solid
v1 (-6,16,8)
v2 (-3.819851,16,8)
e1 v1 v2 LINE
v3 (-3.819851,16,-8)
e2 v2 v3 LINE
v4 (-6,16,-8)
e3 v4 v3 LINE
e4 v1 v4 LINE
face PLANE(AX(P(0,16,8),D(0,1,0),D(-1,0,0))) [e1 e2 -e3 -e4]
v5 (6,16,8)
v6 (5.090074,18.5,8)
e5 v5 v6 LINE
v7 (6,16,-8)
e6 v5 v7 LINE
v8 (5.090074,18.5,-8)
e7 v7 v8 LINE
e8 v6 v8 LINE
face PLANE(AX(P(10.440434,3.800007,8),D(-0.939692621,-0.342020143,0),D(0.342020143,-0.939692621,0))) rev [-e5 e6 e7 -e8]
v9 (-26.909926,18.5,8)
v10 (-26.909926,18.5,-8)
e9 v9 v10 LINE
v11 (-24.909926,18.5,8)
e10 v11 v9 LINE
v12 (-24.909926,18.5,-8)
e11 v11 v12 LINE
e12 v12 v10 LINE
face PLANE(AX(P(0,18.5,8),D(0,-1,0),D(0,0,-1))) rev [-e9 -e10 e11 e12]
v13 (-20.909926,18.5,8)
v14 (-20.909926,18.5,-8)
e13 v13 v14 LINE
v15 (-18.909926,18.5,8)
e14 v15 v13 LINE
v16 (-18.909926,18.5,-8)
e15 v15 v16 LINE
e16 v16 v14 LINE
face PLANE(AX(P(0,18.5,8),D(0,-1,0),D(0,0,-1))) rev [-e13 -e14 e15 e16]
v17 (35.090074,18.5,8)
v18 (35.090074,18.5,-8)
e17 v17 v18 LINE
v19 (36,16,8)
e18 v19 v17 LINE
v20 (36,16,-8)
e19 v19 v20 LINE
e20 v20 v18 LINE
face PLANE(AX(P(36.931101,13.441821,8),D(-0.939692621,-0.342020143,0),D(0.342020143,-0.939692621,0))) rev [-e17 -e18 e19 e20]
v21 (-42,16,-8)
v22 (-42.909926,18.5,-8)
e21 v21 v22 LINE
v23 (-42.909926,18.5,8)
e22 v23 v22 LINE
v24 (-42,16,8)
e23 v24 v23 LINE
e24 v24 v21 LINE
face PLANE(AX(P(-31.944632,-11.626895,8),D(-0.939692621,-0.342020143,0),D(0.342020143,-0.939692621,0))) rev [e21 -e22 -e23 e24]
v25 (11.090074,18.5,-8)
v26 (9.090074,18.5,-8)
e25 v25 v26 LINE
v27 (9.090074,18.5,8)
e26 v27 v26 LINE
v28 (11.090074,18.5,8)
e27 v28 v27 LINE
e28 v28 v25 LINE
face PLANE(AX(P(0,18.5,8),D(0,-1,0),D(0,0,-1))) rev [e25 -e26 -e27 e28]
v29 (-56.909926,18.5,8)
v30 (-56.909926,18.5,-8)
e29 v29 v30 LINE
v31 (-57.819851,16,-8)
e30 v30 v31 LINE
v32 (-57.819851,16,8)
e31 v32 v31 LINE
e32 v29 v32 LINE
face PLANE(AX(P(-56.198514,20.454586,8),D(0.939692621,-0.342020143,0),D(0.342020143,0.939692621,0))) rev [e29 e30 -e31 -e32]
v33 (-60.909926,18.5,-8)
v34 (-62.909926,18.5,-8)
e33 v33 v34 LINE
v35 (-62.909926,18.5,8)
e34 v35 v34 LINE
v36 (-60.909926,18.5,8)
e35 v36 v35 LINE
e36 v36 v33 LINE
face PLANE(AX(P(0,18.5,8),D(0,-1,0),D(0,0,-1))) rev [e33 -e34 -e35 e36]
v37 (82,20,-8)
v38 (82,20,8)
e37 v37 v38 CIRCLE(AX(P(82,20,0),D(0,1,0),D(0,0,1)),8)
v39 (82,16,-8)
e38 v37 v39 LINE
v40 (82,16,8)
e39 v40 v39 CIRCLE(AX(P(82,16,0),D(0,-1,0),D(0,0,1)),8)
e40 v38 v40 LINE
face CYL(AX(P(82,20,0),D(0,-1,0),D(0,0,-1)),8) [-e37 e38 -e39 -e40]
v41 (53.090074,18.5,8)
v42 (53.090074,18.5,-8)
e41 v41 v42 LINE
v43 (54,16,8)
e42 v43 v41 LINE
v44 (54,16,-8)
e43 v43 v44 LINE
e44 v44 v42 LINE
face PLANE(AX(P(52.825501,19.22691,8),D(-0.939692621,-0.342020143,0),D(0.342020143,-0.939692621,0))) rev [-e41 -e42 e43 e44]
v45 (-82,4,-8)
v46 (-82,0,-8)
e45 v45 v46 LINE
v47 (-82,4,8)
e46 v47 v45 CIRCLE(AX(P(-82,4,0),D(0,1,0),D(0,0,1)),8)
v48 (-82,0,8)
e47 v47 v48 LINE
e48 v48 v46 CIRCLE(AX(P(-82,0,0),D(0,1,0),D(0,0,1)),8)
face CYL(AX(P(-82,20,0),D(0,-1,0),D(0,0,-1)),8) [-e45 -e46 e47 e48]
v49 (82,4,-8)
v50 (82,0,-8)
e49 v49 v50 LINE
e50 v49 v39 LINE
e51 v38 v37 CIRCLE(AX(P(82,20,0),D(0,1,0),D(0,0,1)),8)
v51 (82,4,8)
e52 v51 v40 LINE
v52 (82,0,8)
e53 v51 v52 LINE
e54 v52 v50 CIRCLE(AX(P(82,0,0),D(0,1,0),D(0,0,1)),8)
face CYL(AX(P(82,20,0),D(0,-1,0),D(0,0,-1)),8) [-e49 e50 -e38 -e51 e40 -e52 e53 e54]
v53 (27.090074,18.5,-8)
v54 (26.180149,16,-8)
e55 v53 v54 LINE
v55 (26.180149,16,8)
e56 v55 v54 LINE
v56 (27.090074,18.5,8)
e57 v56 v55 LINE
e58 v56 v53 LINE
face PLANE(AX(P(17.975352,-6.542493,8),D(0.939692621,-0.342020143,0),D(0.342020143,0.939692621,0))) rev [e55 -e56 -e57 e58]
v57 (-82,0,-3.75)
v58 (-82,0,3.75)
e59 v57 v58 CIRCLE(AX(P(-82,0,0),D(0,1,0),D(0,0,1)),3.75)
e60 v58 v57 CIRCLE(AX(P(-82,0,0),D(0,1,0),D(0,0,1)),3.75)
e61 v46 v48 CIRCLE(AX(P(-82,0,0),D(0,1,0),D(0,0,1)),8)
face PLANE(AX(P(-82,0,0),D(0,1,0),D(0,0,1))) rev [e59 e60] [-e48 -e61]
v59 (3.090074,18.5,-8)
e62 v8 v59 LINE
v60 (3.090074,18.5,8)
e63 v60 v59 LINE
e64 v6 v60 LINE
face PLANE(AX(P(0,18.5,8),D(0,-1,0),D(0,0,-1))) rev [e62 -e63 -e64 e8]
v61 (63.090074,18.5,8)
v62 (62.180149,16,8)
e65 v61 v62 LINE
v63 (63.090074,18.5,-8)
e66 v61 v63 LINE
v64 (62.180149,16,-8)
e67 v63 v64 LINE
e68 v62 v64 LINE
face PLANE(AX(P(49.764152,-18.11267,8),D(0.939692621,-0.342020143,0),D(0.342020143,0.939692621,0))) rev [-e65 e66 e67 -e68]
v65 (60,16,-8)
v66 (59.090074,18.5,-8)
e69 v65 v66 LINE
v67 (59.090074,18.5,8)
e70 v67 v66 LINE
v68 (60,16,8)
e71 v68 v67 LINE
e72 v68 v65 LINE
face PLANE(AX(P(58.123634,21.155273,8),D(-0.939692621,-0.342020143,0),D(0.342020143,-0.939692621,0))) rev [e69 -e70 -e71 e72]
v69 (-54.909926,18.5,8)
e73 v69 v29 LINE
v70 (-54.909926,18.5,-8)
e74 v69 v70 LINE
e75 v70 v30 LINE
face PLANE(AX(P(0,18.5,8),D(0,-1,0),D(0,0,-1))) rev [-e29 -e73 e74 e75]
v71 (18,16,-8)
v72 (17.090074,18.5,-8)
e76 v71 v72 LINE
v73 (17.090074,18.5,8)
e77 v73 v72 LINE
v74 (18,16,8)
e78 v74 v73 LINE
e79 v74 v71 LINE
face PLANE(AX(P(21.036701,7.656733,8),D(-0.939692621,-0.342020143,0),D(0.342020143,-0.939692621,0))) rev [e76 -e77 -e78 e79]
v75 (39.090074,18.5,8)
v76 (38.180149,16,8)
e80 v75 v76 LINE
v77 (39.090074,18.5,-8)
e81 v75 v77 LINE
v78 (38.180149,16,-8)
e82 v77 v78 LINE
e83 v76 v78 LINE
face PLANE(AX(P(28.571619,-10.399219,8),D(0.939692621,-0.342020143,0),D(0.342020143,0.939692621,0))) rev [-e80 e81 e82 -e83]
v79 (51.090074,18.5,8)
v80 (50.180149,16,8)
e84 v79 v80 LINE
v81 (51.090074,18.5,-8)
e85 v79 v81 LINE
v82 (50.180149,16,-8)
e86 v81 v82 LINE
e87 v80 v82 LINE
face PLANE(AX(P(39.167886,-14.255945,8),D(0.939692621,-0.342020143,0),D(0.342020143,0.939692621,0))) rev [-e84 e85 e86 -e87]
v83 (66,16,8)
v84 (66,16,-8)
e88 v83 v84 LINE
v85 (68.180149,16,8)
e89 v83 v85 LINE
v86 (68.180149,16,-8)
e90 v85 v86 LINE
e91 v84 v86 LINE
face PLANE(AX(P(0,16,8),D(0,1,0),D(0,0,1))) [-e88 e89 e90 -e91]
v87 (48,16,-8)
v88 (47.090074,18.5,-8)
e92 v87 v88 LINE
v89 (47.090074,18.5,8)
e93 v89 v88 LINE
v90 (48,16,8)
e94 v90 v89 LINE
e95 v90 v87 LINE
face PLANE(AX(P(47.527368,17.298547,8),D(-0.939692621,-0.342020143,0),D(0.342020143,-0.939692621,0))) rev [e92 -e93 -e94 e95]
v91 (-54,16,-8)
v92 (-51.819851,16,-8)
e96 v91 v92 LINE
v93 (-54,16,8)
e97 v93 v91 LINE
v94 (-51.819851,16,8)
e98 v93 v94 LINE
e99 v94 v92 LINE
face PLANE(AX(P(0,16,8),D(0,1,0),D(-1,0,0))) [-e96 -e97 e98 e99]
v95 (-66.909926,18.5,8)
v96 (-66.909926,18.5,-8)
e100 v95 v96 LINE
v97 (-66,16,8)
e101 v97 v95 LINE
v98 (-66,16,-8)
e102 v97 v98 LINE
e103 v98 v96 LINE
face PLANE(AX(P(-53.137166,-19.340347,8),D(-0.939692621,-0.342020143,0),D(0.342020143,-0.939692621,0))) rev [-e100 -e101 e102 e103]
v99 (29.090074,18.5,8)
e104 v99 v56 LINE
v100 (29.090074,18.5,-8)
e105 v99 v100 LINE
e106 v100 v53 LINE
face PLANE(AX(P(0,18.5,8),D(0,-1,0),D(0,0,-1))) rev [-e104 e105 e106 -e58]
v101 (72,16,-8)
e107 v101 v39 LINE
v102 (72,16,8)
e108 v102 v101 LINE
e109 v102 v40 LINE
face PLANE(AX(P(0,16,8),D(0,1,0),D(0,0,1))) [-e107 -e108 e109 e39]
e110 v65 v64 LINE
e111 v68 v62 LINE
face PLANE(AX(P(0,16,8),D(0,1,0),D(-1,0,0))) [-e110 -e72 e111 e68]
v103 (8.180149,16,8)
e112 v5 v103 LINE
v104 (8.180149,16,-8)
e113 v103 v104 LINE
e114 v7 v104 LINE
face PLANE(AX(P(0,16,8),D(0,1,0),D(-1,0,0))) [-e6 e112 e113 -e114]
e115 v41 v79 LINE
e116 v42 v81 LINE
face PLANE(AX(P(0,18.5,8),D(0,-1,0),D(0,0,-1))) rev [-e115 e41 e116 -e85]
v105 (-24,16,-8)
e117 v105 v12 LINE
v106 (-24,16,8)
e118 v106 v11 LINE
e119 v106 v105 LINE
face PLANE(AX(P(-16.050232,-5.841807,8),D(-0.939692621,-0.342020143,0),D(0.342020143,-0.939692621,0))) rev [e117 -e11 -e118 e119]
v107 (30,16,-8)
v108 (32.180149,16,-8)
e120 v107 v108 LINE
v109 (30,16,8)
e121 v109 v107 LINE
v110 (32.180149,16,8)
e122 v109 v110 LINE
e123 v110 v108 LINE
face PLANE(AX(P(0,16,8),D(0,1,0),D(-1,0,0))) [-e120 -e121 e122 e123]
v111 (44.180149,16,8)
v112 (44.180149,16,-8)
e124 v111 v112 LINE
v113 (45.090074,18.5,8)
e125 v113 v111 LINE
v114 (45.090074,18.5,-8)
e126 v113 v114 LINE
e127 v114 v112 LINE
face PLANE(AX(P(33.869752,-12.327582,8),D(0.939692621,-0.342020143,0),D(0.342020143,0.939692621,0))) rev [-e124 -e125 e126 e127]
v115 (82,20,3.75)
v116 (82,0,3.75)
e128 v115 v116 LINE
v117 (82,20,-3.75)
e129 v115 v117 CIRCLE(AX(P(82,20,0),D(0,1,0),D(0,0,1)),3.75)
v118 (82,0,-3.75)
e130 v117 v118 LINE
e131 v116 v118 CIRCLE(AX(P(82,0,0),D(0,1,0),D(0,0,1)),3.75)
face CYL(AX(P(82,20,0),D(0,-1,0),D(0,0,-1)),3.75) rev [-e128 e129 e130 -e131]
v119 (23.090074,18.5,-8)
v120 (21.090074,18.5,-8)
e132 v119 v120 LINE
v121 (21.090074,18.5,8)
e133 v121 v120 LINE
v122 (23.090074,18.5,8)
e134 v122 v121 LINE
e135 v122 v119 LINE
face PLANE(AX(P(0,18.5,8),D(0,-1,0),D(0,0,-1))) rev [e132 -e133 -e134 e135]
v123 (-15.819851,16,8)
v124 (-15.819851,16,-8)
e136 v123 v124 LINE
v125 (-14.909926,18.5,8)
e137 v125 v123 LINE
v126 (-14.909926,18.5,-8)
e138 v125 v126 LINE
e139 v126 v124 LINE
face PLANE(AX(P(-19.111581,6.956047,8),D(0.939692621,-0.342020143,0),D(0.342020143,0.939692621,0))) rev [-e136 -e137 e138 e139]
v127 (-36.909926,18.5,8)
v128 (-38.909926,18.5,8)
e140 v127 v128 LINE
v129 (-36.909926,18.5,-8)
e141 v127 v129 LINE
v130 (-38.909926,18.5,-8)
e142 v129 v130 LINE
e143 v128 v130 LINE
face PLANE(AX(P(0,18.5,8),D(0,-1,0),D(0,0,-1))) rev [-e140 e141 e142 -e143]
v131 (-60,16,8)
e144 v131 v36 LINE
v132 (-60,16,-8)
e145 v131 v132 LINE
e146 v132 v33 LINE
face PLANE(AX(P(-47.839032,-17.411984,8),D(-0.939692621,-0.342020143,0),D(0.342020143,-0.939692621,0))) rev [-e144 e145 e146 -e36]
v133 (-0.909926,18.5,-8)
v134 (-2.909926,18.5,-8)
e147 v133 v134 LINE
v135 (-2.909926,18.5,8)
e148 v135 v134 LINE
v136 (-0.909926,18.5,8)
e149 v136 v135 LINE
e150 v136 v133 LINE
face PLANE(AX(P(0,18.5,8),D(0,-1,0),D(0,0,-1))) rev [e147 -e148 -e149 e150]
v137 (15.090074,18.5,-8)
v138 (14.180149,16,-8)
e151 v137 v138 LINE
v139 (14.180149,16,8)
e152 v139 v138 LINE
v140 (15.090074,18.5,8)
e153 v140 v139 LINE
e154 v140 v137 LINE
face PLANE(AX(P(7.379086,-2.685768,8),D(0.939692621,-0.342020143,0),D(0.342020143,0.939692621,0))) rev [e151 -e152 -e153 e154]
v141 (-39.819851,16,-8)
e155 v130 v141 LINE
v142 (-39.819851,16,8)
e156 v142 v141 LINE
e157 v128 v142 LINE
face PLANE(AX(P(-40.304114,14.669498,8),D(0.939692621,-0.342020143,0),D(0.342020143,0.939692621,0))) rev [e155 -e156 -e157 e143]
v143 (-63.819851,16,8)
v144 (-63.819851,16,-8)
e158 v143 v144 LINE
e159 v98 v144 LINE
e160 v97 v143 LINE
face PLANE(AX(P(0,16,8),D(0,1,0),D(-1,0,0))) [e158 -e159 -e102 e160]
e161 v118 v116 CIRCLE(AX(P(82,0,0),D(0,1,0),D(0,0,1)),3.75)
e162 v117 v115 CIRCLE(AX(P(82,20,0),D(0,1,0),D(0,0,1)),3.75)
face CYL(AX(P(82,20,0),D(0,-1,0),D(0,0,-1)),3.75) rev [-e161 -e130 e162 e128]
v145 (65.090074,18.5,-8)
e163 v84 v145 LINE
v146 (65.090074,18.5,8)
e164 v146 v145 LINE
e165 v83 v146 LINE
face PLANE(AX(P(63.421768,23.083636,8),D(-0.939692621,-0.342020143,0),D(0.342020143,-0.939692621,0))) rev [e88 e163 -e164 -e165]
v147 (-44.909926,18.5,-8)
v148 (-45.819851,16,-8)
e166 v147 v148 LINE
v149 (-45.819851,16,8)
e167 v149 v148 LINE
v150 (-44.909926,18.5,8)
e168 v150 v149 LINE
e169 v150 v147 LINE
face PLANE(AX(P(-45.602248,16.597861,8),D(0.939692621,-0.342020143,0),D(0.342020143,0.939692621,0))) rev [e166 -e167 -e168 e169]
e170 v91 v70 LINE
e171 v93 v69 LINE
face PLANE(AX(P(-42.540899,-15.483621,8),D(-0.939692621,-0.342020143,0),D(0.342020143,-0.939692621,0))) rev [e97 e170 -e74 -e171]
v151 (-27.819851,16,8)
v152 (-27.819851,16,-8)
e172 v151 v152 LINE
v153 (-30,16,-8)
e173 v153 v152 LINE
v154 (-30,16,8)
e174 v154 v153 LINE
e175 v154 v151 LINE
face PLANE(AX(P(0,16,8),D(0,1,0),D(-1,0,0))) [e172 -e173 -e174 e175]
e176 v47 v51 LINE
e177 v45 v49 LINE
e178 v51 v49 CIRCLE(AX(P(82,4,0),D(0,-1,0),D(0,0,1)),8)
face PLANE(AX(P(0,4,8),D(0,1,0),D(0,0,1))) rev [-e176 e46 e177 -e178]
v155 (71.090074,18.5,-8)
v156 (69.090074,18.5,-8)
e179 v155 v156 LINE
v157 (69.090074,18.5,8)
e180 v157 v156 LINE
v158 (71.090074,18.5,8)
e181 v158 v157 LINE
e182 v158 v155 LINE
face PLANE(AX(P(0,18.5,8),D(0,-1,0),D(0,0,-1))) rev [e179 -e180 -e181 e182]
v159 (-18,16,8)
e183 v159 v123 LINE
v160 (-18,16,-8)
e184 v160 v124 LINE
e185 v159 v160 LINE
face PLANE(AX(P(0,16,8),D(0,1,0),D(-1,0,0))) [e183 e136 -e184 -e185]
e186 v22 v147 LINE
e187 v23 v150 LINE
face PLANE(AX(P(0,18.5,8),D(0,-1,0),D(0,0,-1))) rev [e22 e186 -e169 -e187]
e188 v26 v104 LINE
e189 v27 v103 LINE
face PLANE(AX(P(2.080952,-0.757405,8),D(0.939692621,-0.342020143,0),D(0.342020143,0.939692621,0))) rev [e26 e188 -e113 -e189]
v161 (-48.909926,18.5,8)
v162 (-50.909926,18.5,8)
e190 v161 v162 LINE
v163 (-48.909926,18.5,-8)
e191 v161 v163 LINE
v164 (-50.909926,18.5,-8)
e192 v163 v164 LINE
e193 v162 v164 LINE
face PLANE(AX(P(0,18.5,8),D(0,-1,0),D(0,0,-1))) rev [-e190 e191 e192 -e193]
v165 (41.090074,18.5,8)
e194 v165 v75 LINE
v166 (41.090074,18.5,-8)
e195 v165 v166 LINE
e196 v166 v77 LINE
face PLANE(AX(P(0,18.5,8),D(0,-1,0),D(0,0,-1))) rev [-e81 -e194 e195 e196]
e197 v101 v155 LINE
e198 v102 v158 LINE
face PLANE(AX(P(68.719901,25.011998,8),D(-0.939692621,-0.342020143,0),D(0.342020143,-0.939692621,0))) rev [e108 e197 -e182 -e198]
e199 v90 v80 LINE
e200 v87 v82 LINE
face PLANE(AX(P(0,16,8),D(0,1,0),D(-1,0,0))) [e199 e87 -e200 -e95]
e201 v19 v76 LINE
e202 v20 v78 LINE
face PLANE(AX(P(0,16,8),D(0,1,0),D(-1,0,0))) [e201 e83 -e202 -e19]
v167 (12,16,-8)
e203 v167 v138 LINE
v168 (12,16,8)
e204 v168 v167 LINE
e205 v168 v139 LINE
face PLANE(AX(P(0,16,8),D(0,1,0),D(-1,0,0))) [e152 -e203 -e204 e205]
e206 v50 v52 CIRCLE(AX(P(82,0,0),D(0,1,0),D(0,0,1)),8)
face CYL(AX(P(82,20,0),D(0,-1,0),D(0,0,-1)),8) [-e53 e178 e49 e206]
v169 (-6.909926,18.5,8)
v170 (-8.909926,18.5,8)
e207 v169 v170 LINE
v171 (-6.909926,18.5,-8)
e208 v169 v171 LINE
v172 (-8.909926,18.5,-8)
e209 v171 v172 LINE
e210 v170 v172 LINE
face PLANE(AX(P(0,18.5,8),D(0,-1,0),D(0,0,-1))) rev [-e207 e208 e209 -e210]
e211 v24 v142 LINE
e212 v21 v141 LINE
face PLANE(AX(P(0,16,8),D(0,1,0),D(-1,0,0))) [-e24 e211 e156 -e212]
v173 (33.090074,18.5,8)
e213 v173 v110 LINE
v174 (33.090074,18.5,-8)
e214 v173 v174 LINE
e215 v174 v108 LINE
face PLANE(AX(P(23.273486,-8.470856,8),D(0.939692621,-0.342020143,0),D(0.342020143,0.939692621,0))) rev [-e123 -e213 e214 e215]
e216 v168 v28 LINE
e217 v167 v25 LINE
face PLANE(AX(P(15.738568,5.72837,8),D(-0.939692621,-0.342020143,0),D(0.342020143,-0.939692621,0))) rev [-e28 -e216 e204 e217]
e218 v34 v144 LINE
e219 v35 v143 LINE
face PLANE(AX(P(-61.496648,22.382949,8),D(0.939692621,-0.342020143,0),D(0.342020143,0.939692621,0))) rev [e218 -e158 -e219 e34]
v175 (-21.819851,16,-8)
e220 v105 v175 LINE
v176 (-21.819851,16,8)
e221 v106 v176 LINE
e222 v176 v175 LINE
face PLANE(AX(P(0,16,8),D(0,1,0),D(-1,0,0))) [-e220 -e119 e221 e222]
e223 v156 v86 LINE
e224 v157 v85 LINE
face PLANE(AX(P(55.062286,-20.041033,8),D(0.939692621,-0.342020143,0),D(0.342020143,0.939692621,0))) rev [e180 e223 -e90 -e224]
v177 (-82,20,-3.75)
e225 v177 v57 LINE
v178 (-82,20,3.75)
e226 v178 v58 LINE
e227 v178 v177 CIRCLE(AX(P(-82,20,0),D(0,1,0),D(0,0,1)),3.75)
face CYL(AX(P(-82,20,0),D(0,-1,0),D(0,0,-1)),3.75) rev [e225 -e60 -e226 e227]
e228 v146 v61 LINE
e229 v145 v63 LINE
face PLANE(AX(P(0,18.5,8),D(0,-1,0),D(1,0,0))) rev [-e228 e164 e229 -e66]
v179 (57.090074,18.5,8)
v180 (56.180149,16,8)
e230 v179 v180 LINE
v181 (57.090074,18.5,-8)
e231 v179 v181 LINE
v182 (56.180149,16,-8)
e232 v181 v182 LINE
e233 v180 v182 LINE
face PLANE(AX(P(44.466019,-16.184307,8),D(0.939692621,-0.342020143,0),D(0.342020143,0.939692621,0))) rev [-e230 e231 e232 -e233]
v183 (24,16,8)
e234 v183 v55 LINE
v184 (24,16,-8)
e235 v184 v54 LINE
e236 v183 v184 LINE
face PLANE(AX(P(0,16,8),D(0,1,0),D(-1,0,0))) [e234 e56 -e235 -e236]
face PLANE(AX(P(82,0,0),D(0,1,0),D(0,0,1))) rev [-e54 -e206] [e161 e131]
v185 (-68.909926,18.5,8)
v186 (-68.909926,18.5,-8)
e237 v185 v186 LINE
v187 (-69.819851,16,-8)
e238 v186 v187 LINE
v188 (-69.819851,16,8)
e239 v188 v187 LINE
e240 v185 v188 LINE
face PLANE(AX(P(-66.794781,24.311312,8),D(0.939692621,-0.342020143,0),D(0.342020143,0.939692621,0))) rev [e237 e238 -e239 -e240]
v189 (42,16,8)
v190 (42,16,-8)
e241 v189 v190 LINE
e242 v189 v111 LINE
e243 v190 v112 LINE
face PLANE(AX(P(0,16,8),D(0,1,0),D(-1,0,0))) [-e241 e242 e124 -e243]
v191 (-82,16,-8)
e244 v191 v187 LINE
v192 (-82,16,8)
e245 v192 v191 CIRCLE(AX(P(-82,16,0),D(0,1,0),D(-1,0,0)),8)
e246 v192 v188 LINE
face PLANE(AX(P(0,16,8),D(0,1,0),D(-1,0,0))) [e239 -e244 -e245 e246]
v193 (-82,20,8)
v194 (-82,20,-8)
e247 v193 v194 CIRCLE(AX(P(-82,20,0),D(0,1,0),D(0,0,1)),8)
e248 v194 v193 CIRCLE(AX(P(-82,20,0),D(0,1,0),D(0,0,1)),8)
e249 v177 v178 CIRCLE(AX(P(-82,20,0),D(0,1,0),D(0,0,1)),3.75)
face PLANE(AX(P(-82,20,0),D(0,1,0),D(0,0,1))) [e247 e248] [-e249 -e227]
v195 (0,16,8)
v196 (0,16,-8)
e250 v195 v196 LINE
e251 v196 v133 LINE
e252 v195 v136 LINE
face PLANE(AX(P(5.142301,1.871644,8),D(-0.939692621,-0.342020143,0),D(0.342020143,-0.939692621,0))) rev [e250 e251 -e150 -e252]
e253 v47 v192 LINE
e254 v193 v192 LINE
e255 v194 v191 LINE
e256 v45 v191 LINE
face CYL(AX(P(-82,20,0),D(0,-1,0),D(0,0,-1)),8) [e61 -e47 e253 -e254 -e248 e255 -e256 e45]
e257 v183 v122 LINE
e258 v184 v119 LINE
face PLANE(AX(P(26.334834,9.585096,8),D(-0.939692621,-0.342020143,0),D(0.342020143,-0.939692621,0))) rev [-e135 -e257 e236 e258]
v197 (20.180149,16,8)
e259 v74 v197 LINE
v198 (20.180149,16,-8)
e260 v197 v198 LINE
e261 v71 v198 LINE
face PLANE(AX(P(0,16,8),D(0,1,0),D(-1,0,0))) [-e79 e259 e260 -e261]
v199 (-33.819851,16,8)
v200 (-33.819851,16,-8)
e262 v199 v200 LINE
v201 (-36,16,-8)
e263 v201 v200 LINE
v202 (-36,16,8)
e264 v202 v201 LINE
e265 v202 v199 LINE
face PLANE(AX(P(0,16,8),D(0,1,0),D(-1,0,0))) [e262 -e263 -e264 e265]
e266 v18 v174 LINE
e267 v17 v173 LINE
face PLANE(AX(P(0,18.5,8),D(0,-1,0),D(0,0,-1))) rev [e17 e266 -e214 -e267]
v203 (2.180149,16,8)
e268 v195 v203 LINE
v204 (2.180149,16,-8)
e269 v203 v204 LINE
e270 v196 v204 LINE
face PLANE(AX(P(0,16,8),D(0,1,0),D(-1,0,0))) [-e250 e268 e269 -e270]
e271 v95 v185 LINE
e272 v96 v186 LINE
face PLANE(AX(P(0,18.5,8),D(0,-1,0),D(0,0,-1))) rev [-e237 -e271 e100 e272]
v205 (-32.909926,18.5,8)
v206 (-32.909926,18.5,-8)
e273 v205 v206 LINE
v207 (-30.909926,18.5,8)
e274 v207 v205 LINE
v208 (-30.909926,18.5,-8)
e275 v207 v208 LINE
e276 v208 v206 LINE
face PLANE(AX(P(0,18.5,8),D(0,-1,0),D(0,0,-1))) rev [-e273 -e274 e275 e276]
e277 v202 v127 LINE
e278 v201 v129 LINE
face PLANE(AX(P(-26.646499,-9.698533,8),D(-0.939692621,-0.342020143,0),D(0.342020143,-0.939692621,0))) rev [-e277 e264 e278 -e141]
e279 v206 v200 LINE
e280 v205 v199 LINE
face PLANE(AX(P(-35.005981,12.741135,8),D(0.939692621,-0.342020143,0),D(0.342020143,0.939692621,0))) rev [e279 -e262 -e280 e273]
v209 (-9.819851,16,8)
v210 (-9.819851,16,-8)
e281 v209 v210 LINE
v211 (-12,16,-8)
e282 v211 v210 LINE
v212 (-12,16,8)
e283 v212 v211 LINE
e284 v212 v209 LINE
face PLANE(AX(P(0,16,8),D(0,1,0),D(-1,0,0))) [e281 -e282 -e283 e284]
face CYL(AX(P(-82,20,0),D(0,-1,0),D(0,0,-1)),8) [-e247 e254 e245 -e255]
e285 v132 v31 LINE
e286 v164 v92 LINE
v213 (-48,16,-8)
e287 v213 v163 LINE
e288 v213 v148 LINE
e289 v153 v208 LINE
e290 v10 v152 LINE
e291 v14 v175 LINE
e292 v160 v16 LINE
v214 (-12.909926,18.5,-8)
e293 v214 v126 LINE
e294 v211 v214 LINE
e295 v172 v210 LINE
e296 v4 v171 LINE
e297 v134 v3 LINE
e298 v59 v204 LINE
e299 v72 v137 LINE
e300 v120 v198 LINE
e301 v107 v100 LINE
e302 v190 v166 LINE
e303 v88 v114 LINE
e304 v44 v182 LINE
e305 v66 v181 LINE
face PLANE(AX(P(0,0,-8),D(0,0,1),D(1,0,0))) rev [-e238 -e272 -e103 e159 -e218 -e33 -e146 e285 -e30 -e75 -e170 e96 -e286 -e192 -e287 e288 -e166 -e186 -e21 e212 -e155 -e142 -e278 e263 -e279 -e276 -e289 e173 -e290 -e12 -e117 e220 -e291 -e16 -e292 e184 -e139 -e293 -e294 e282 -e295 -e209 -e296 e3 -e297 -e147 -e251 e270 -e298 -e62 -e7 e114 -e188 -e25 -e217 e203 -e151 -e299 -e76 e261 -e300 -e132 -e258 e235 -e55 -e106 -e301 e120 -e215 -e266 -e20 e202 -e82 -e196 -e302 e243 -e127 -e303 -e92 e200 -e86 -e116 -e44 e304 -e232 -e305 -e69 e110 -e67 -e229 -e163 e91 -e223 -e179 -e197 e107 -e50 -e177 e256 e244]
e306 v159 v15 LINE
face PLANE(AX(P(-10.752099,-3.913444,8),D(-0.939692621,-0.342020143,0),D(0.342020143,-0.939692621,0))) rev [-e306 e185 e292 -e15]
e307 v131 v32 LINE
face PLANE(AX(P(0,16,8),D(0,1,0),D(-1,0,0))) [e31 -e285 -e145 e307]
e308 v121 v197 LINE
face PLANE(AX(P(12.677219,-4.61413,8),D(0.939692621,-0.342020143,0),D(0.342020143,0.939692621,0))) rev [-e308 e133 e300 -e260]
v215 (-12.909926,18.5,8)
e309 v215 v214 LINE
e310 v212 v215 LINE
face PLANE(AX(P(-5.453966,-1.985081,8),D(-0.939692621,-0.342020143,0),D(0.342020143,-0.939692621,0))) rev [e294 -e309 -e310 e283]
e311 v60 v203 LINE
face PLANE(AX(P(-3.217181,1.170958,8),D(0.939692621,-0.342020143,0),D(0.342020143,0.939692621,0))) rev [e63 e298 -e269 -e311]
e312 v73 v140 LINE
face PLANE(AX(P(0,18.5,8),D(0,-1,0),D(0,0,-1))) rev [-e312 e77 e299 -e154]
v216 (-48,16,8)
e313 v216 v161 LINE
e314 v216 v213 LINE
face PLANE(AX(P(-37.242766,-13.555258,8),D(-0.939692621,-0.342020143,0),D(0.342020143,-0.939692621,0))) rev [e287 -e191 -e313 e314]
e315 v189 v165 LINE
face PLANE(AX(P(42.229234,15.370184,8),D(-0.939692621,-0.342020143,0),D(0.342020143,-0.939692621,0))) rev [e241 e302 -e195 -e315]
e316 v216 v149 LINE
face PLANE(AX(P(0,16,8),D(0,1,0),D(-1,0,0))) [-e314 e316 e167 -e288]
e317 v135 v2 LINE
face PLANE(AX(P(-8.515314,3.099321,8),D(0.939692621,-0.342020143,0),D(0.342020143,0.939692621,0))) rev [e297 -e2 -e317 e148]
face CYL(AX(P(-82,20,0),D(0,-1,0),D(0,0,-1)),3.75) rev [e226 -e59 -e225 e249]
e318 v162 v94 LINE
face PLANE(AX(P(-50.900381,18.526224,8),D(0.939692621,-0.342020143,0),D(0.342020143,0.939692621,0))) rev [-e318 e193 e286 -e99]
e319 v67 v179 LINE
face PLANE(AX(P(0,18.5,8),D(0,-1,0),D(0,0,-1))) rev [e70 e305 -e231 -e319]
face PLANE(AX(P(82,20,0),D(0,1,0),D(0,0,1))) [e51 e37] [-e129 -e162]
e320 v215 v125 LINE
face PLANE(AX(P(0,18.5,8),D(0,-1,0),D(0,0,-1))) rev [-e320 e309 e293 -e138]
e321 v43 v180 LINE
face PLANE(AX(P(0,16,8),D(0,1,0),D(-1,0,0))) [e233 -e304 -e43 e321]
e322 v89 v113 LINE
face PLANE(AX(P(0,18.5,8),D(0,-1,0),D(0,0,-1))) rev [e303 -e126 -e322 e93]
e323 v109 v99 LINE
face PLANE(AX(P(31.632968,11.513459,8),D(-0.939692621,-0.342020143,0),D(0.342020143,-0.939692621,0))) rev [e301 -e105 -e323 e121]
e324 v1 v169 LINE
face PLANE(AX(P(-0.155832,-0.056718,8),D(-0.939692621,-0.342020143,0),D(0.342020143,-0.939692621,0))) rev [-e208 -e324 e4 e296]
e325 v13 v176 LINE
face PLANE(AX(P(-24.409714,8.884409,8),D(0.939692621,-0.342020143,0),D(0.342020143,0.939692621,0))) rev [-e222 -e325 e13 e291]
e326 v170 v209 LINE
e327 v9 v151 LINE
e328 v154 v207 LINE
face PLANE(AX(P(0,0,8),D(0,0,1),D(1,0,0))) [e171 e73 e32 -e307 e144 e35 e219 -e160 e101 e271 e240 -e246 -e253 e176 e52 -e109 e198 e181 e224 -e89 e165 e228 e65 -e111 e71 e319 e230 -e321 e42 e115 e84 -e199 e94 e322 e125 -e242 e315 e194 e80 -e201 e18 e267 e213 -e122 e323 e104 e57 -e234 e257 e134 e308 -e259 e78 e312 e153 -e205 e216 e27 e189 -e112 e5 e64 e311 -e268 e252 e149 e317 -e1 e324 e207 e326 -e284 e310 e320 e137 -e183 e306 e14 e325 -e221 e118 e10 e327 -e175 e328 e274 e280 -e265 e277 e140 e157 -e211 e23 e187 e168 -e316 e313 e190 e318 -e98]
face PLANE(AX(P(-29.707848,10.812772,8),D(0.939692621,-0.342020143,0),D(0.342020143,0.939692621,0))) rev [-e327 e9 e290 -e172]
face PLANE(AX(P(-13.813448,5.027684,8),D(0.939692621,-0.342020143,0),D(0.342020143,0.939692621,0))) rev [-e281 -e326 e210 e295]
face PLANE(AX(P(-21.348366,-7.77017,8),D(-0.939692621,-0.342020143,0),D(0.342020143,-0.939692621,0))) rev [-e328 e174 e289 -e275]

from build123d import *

# Parameters (mm, degrees)
END_BOSSES_SKETCH_R   = 8
END_BOSSES_SKETCH_R_2 = 3.75
END_BOSSES_DEPTH      = 20
END_BOSSES_2_DEPTH    = 20
RACK_TEETH_24X_DEPTH  = 8
PIN_START             = -36
PIN_HOLES_SKETCH_R    = 3.75
PIN_HOLES_2X_DEPTH    = 36


with BuildPart() as part:
    # End Bosses Sketch → End Bosses (new body)
    with BuildSketch(Plane(origin=(0, 0, 0), x_dir=(1, 0, 0), z_dir=(0, 1, 0))):
        with Locations(Location((-82, 0, 0), (0, 0, 270))):
            Circle(END_BOSSES_SKETCH_R)
        with Locations(Location((-82, 0, 0), (0, 0, 270))):
            Circle(END_BOSSES_SKETCH_R_2, mode=Mode.SUBTRACT)
    extrude(amount=END_BOSSES_DEPTH)



with BuildPart() as body_2:
    # End Bosses Sketch → End Bosses 2 (new body)
    with BuildSketch(Plane(origin=(0, 0, 0), x_dir=(1, 0, 0), z_dir=(0, 1, 0))):
        with Locations(Location((82, 0, 0), (0, 0, 270))):
            Circle(END_BOSSES_SKETCH_R)
        with Locations(Location((82, 0, 0), (0, 0, 270))):
            Circle(END_BOSSES_SKETCH_R_2, mode=Mode.SUBTRACT)
    extrude(amount=END_BOSSES_2_DEPTH)


with BuildPart() as part_1:
    add(part.part)

    add(body_2.part)  # Rack Teeth 24x merges body 2
    # Rack Tooth Profile Sketch → Rack Teeth 24x (add, symmetric)
    with BuildSketch(Plane.XY):
        Polygon((-82, 4), (82, 4), (82, 16), (72, 16), (71.090074414, 18.5), (69.090074414, 18.5), (68.180148829, 16), (66, 16), (65.090074414, 18.5), (63.090074414, 18.5), (62.180148829, 16), (60, 16), (59.090074414, 18.5), (57.090074414, 18.5), (56.180148829, 16), (54, 16), (53.090074414, 18.5), (51.090074414, 18.5), (50.180148829, 16), (48, 16), (47.090074414, 18.5), (45.090074414, 18.5), (44.180148829, 16), (42, 16), (41.090074414, 18.5), (39.090074414, 18.5), (38.180148829, 16), (36, 16), (35.090074414, 18.5), (33.090074414, 18.5), (32.180148829, 16), (30, 16), (29.090074414, 18.5), (27.090074414, 18.5), (26.180148829, 16), (24, 16), (23.090074414, 18.5), (21.090074414, 18.5), (20.180148829, 16), (18, 16), (17.090074414, 18.5), (15.090074414, 18.5), (14.180148829, 16), (12, 16), (11.090074414, 18.5), (9.090074414, 18.5), (8.180148829, 16), (6, 16), (5.090074414, 18.5), (3.090074414, 18.5), (2.180148829, 16), (0, 16), (-0.909925586, 18.5), (-2.909925586, 18.5), (-3.819851171, 16), (-6, 16), (-6.909925586, 18.5), (-8.909925586, 18.5), (-9.819851171, 16), (-12, 16), (-12.909925586, 18.5), (-14.909925586, 18.5), (-15.819851171, 16), (-18, 16), (-18.909925586, 18.5), (-20.909925586, 18.5), (-21.819851171, 16), (-24, 16), (-24.909925586, 18.5), (-26.909925586, 18.5), (-27.819851171, 16), (-30, 16), (-30.909925586, 18.5), (-32.909925586, 18.5), (-33.819851171, 16), (-36, 16), (-36.909925586, 18.5), (-38.909925586, 18.5), (-39.819851171, 16), (-42, 16), (-42.909925586, 18.5), (-44.909925586, 18.5), (-45.819851171, 16), (-48, 16), (-48.909925586, 18.5), (-50.909925586, 18.5), (-51.819851171, 16), (-54, 16), (-54.909925586, 18.5), (-56.909925586, 18.5), (-57.819851171, 16), (-60, 16), (-60.909925586, 18.5), (-62.909925586, 18.5), (-63.819851171, 16), (-66, 16), (-66.909925586, 18.5), (-68.909925586, 18.5), (-69.819851171, 16), (-82, 16), align=None)
    extrude(amount=RACK_TEETH_24X_DEPTH, both=True)

    # Pin Holes Sketch → Pin Holes 2x (cut)
    with BuildSketch(Plane(origin=(0, 20, 0), x_dir=(1, 0, 0), z_dir=(0, 1, 0)).offset(PIN_START)):
        with Locations(Location((-82, 0, 0), (0, 0, 270))):
            Circle(PIN_HOLES_SKETCH_R)
        with Locations(Location((82, 0, 0), (0, 0, 270))):
            Circle(PIN_HOLES_SKETCH_R)
    extrude(amount=PIN_HOLES_2X_DEPTH, mode=Mode.SUBTRACT)


solid = part_1.part
